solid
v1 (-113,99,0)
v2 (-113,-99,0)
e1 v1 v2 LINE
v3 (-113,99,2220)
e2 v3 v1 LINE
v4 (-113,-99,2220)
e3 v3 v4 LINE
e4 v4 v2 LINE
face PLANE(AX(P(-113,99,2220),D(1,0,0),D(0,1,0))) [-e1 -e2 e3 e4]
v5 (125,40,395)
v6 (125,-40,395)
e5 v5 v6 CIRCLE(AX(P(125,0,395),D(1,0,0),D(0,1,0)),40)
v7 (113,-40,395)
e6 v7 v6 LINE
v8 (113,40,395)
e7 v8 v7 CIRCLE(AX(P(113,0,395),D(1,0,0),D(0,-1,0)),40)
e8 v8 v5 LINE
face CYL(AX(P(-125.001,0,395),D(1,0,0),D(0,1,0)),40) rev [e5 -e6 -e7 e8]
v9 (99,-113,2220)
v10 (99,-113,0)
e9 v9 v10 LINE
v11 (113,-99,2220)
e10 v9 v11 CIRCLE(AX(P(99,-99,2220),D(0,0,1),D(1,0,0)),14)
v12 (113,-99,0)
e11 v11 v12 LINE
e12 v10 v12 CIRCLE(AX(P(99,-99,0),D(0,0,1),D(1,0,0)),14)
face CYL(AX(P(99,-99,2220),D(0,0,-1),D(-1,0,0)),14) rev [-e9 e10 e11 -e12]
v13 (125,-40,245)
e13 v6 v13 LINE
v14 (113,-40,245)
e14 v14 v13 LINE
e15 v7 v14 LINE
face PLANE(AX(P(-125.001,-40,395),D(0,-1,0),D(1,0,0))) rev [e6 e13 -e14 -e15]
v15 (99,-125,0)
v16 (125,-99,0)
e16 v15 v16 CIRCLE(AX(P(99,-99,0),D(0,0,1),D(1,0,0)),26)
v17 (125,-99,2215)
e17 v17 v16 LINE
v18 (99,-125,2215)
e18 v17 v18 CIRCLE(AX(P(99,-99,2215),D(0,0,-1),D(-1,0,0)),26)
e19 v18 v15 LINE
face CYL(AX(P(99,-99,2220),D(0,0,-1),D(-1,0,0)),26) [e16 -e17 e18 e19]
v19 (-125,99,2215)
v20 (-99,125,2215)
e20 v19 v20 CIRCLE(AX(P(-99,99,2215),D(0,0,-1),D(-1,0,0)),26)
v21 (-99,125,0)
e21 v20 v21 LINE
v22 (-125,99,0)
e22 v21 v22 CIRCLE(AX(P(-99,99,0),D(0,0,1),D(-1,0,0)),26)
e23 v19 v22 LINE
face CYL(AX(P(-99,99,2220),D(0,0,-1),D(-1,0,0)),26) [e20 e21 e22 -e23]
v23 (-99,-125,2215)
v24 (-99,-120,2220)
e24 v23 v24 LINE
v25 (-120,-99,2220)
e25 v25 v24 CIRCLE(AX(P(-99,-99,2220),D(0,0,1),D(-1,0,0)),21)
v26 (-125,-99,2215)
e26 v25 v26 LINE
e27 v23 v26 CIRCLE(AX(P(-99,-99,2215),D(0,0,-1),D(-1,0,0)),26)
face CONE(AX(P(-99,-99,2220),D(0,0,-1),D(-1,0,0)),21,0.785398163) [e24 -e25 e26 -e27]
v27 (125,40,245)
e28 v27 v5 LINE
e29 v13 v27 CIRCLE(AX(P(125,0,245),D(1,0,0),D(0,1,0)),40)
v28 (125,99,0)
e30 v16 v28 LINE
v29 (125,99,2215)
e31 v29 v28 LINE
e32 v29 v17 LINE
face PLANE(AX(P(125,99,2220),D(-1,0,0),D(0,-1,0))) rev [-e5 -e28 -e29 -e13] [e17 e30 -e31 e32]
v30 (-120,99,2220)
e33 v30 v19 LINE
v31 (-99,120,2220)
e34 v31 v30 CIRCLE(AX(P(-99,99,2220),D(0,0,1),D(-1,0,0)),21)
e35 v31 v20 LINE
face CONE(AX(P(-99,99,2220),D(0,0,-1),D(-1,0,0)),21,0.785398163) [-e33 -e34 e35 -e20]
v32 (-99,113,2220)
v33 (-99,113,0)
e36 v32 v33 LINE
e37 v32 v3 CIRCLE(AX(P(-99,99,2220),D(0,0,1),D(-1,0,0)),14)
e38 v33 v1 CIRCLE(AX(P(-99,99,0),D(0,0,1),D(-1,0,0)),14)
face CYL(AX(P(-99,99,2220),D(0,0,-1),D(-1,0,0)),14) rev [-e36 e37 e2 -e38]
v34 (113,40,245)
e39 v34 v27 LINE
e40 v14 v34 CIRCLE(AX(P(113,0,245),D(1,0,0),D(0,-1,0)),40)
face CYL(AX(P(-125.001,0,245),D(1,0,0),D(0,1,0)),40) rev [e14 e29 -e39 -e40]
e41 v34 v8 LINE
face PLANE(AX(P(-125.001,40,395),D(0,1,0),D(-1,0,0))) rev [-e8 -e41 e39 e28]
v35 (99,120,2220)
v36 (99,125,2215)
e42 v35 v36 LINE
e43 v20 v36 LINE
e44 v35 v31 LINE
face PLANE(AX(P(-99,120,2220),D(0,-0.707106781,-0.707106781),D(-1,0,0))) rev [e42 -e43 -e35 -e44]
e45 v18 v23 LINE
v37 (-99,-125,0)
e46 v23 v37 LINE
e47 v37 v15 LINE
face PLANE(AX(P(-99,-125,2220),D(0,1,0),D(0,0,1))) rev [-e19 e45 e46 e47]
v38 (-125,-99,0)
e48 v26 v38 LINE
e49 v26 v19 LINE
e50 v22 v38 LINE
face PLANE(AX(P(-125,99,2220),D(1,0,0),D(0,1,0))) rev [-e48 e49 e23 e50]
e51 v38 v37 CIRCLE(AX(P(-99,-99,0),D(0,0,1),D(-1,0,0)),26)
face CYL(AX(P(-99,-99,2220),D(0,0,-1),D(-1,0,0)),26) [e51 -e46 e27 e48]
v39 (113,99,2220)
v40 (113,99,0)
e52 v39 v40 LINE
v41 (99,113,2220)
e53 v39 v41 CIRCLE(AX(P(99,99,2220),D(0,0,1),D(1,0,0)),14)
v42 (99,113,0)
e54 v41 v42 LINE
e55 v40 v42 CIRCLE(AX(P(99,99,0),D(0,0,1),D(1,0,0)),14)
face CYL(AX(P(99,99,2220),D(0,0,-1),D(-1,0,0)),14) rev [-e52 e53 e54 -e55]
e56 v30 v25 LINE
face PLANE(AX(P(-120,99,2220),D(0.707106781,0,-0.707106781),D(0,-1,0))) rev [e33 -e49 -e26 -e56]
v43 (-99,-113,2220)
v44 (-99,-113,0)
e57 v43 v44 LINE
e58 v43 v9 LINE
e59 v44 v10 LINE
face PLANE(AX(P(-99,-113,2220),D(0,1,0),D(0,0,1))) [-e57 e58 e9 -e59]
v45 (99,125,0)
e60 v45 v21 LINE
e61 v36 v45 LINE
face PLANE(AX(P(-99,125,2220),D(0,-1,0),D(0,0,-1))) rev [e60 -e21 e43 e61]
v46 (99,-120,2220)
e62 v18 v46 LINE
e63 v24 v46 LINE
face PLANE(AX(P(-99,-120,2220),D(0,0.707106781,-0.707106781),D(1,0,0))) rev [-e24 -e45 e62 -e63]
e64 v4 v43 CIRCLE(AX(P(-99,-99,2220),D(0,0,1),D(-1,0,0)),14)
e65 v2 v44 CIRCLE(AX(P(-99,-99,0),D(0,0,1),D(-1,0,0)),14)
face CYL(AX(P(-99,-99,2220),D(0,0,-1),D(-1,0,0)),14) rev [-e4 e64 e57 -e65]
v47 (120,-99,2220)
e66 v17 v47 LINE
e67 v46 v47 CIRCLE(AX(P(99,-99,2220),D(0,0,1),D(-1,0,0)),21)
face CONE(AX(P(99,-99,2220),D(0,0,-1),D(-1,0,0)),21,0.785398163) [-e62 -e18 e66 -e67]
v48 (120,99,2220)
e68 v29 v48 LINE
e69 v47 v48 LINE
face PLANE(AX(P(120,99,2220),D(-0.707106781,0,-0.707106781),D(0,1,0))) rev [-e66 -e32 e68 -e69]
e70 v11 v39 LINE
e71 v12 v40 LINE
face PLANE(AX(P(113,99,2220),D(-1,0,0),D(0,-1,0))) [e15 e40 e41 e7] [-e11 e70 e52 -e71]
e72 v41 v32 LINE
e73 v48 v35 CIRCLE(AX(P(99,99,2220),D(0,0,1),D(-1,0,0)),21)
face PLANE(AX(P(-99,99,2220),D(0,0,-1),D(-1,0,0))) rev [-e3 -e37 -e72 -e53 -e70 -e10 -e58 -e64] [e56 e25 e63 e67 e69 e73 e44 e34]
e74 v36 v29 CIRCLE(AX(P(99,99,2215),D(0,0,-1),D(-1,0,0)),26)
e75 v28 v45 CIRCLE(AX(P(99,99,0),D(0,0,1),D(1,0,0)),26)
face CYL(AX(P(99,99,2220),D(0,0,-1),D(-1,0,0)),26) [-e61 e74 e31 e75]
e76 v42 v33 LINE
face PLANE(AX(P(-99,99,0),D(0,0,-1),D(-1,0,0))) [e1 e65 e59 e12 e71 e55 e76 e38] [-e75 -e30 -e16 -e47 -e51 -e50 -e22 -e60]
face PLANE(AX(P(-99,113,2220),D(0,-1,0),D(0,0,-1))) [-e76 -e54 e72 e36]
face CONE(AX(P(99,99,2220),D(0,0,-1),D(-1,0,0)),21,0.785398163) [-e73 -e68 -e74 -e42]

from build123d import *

# Parameters (mm, degrees)
EXTRUDE_1_DEPTH     = 2220
CHAMFER_1_SIZE      = 5
CUT_EXTRUDE_1_REACH = 2239.527


with BuildPart() as part:
    # 草图1 → 凸台-拉伸1 (new body)
    with BuildSketch(Plane.XY):
        with BuildLine():
            Line((-99, 125), (99, 125))
            ThreePointArc((99, 125), (117.384776311, 117.384776311), (125, 99))
            Line((125, 99), (125, -99))
            ThreePointArc((125, -99), (117.384776311, -117.384776311), (99, -125))
            Line((99, -125), (-99, -125))
            ThreePointArc((-99, -125), (-117.384776311, -117.384776311), (-125, -99))
            Line((-125, -99), (-125, 99))
            ThreePointArc((-125, 99), (-117.384776311, 117.384776311), (-99, 125))
        make_face()
        with BuildLine():
            Line((-99, 113), (99, 113))
            ThreePointArc((99, 113), (108.899494937, 108.899494937), (113, 99))
            Line((113, 99), (113, -99))
            ThreePointArc((113, -99), (108.899494937, -108.899494937), (99, -113))
            Line((99, -113), (-99, -113))
            ThreePointArc((-99, -113), (-108.899494937, -108.899494937), (-113, -99))
            Line((-113, -99), (-113, 99))
            ThreePointArc((-113, 99), (-108.899494937, 108.899494937), (-99, 113))
        make_face(mode=Mode.SUBTRACT)
    extrude(amount=EXTRUDE_1_DEPTH)

    # 倒角1
    chamfer_1_edges = [part.edges().sort_by_distance(p)[0] for p in [
        (-117.384776311, -117.384776311, 2220),
        (0, -125, 2220),
        (117.384776311, -117.384776311, 2220),
        (125, 0, 2220),
        (117.384776311, 117.384776311, 2220),
        (0, 125, 2220),
        (-117.384776311, 117.384776311, 2220),
        (-125, 0, 2220),
    ]]
    chamfer(chamfer_1_edges, length=CHAMFER_1_SIZE)

    # 草图2 → 切除-拉伸1 (cut, up to next)
    with BuildSketch(Plane(origin=(125, 0, 0), x_dir=(0, 0, -1), z_dir=(1, 0, 0)), mode=Mode.PRIVATE) as cut_extrude_1_sk1:
        with BuildLine():
            Line((-395, 40), (-245, 40))
            ThreePointArc((-245, 40), (-205, 0), (-245, -40))
            Line((-245, -40), (-395, -40))
            ThreePointArc((-395, -40), (-435, 0), (-395, 40))
        make_face()
    cut_extrude_1_tool1 = extrude(cut_extrude_1_sk1.sketch, amount=-CUT_EXTRUDE_1_REACH, mode=Mode.PRIVATE) & part.part
    add(cut_extrude_1_tool1.solids().sort_by_distance((125, 0, 320))[0], mode=Mode.SUBTRACT)


solid = part.part
